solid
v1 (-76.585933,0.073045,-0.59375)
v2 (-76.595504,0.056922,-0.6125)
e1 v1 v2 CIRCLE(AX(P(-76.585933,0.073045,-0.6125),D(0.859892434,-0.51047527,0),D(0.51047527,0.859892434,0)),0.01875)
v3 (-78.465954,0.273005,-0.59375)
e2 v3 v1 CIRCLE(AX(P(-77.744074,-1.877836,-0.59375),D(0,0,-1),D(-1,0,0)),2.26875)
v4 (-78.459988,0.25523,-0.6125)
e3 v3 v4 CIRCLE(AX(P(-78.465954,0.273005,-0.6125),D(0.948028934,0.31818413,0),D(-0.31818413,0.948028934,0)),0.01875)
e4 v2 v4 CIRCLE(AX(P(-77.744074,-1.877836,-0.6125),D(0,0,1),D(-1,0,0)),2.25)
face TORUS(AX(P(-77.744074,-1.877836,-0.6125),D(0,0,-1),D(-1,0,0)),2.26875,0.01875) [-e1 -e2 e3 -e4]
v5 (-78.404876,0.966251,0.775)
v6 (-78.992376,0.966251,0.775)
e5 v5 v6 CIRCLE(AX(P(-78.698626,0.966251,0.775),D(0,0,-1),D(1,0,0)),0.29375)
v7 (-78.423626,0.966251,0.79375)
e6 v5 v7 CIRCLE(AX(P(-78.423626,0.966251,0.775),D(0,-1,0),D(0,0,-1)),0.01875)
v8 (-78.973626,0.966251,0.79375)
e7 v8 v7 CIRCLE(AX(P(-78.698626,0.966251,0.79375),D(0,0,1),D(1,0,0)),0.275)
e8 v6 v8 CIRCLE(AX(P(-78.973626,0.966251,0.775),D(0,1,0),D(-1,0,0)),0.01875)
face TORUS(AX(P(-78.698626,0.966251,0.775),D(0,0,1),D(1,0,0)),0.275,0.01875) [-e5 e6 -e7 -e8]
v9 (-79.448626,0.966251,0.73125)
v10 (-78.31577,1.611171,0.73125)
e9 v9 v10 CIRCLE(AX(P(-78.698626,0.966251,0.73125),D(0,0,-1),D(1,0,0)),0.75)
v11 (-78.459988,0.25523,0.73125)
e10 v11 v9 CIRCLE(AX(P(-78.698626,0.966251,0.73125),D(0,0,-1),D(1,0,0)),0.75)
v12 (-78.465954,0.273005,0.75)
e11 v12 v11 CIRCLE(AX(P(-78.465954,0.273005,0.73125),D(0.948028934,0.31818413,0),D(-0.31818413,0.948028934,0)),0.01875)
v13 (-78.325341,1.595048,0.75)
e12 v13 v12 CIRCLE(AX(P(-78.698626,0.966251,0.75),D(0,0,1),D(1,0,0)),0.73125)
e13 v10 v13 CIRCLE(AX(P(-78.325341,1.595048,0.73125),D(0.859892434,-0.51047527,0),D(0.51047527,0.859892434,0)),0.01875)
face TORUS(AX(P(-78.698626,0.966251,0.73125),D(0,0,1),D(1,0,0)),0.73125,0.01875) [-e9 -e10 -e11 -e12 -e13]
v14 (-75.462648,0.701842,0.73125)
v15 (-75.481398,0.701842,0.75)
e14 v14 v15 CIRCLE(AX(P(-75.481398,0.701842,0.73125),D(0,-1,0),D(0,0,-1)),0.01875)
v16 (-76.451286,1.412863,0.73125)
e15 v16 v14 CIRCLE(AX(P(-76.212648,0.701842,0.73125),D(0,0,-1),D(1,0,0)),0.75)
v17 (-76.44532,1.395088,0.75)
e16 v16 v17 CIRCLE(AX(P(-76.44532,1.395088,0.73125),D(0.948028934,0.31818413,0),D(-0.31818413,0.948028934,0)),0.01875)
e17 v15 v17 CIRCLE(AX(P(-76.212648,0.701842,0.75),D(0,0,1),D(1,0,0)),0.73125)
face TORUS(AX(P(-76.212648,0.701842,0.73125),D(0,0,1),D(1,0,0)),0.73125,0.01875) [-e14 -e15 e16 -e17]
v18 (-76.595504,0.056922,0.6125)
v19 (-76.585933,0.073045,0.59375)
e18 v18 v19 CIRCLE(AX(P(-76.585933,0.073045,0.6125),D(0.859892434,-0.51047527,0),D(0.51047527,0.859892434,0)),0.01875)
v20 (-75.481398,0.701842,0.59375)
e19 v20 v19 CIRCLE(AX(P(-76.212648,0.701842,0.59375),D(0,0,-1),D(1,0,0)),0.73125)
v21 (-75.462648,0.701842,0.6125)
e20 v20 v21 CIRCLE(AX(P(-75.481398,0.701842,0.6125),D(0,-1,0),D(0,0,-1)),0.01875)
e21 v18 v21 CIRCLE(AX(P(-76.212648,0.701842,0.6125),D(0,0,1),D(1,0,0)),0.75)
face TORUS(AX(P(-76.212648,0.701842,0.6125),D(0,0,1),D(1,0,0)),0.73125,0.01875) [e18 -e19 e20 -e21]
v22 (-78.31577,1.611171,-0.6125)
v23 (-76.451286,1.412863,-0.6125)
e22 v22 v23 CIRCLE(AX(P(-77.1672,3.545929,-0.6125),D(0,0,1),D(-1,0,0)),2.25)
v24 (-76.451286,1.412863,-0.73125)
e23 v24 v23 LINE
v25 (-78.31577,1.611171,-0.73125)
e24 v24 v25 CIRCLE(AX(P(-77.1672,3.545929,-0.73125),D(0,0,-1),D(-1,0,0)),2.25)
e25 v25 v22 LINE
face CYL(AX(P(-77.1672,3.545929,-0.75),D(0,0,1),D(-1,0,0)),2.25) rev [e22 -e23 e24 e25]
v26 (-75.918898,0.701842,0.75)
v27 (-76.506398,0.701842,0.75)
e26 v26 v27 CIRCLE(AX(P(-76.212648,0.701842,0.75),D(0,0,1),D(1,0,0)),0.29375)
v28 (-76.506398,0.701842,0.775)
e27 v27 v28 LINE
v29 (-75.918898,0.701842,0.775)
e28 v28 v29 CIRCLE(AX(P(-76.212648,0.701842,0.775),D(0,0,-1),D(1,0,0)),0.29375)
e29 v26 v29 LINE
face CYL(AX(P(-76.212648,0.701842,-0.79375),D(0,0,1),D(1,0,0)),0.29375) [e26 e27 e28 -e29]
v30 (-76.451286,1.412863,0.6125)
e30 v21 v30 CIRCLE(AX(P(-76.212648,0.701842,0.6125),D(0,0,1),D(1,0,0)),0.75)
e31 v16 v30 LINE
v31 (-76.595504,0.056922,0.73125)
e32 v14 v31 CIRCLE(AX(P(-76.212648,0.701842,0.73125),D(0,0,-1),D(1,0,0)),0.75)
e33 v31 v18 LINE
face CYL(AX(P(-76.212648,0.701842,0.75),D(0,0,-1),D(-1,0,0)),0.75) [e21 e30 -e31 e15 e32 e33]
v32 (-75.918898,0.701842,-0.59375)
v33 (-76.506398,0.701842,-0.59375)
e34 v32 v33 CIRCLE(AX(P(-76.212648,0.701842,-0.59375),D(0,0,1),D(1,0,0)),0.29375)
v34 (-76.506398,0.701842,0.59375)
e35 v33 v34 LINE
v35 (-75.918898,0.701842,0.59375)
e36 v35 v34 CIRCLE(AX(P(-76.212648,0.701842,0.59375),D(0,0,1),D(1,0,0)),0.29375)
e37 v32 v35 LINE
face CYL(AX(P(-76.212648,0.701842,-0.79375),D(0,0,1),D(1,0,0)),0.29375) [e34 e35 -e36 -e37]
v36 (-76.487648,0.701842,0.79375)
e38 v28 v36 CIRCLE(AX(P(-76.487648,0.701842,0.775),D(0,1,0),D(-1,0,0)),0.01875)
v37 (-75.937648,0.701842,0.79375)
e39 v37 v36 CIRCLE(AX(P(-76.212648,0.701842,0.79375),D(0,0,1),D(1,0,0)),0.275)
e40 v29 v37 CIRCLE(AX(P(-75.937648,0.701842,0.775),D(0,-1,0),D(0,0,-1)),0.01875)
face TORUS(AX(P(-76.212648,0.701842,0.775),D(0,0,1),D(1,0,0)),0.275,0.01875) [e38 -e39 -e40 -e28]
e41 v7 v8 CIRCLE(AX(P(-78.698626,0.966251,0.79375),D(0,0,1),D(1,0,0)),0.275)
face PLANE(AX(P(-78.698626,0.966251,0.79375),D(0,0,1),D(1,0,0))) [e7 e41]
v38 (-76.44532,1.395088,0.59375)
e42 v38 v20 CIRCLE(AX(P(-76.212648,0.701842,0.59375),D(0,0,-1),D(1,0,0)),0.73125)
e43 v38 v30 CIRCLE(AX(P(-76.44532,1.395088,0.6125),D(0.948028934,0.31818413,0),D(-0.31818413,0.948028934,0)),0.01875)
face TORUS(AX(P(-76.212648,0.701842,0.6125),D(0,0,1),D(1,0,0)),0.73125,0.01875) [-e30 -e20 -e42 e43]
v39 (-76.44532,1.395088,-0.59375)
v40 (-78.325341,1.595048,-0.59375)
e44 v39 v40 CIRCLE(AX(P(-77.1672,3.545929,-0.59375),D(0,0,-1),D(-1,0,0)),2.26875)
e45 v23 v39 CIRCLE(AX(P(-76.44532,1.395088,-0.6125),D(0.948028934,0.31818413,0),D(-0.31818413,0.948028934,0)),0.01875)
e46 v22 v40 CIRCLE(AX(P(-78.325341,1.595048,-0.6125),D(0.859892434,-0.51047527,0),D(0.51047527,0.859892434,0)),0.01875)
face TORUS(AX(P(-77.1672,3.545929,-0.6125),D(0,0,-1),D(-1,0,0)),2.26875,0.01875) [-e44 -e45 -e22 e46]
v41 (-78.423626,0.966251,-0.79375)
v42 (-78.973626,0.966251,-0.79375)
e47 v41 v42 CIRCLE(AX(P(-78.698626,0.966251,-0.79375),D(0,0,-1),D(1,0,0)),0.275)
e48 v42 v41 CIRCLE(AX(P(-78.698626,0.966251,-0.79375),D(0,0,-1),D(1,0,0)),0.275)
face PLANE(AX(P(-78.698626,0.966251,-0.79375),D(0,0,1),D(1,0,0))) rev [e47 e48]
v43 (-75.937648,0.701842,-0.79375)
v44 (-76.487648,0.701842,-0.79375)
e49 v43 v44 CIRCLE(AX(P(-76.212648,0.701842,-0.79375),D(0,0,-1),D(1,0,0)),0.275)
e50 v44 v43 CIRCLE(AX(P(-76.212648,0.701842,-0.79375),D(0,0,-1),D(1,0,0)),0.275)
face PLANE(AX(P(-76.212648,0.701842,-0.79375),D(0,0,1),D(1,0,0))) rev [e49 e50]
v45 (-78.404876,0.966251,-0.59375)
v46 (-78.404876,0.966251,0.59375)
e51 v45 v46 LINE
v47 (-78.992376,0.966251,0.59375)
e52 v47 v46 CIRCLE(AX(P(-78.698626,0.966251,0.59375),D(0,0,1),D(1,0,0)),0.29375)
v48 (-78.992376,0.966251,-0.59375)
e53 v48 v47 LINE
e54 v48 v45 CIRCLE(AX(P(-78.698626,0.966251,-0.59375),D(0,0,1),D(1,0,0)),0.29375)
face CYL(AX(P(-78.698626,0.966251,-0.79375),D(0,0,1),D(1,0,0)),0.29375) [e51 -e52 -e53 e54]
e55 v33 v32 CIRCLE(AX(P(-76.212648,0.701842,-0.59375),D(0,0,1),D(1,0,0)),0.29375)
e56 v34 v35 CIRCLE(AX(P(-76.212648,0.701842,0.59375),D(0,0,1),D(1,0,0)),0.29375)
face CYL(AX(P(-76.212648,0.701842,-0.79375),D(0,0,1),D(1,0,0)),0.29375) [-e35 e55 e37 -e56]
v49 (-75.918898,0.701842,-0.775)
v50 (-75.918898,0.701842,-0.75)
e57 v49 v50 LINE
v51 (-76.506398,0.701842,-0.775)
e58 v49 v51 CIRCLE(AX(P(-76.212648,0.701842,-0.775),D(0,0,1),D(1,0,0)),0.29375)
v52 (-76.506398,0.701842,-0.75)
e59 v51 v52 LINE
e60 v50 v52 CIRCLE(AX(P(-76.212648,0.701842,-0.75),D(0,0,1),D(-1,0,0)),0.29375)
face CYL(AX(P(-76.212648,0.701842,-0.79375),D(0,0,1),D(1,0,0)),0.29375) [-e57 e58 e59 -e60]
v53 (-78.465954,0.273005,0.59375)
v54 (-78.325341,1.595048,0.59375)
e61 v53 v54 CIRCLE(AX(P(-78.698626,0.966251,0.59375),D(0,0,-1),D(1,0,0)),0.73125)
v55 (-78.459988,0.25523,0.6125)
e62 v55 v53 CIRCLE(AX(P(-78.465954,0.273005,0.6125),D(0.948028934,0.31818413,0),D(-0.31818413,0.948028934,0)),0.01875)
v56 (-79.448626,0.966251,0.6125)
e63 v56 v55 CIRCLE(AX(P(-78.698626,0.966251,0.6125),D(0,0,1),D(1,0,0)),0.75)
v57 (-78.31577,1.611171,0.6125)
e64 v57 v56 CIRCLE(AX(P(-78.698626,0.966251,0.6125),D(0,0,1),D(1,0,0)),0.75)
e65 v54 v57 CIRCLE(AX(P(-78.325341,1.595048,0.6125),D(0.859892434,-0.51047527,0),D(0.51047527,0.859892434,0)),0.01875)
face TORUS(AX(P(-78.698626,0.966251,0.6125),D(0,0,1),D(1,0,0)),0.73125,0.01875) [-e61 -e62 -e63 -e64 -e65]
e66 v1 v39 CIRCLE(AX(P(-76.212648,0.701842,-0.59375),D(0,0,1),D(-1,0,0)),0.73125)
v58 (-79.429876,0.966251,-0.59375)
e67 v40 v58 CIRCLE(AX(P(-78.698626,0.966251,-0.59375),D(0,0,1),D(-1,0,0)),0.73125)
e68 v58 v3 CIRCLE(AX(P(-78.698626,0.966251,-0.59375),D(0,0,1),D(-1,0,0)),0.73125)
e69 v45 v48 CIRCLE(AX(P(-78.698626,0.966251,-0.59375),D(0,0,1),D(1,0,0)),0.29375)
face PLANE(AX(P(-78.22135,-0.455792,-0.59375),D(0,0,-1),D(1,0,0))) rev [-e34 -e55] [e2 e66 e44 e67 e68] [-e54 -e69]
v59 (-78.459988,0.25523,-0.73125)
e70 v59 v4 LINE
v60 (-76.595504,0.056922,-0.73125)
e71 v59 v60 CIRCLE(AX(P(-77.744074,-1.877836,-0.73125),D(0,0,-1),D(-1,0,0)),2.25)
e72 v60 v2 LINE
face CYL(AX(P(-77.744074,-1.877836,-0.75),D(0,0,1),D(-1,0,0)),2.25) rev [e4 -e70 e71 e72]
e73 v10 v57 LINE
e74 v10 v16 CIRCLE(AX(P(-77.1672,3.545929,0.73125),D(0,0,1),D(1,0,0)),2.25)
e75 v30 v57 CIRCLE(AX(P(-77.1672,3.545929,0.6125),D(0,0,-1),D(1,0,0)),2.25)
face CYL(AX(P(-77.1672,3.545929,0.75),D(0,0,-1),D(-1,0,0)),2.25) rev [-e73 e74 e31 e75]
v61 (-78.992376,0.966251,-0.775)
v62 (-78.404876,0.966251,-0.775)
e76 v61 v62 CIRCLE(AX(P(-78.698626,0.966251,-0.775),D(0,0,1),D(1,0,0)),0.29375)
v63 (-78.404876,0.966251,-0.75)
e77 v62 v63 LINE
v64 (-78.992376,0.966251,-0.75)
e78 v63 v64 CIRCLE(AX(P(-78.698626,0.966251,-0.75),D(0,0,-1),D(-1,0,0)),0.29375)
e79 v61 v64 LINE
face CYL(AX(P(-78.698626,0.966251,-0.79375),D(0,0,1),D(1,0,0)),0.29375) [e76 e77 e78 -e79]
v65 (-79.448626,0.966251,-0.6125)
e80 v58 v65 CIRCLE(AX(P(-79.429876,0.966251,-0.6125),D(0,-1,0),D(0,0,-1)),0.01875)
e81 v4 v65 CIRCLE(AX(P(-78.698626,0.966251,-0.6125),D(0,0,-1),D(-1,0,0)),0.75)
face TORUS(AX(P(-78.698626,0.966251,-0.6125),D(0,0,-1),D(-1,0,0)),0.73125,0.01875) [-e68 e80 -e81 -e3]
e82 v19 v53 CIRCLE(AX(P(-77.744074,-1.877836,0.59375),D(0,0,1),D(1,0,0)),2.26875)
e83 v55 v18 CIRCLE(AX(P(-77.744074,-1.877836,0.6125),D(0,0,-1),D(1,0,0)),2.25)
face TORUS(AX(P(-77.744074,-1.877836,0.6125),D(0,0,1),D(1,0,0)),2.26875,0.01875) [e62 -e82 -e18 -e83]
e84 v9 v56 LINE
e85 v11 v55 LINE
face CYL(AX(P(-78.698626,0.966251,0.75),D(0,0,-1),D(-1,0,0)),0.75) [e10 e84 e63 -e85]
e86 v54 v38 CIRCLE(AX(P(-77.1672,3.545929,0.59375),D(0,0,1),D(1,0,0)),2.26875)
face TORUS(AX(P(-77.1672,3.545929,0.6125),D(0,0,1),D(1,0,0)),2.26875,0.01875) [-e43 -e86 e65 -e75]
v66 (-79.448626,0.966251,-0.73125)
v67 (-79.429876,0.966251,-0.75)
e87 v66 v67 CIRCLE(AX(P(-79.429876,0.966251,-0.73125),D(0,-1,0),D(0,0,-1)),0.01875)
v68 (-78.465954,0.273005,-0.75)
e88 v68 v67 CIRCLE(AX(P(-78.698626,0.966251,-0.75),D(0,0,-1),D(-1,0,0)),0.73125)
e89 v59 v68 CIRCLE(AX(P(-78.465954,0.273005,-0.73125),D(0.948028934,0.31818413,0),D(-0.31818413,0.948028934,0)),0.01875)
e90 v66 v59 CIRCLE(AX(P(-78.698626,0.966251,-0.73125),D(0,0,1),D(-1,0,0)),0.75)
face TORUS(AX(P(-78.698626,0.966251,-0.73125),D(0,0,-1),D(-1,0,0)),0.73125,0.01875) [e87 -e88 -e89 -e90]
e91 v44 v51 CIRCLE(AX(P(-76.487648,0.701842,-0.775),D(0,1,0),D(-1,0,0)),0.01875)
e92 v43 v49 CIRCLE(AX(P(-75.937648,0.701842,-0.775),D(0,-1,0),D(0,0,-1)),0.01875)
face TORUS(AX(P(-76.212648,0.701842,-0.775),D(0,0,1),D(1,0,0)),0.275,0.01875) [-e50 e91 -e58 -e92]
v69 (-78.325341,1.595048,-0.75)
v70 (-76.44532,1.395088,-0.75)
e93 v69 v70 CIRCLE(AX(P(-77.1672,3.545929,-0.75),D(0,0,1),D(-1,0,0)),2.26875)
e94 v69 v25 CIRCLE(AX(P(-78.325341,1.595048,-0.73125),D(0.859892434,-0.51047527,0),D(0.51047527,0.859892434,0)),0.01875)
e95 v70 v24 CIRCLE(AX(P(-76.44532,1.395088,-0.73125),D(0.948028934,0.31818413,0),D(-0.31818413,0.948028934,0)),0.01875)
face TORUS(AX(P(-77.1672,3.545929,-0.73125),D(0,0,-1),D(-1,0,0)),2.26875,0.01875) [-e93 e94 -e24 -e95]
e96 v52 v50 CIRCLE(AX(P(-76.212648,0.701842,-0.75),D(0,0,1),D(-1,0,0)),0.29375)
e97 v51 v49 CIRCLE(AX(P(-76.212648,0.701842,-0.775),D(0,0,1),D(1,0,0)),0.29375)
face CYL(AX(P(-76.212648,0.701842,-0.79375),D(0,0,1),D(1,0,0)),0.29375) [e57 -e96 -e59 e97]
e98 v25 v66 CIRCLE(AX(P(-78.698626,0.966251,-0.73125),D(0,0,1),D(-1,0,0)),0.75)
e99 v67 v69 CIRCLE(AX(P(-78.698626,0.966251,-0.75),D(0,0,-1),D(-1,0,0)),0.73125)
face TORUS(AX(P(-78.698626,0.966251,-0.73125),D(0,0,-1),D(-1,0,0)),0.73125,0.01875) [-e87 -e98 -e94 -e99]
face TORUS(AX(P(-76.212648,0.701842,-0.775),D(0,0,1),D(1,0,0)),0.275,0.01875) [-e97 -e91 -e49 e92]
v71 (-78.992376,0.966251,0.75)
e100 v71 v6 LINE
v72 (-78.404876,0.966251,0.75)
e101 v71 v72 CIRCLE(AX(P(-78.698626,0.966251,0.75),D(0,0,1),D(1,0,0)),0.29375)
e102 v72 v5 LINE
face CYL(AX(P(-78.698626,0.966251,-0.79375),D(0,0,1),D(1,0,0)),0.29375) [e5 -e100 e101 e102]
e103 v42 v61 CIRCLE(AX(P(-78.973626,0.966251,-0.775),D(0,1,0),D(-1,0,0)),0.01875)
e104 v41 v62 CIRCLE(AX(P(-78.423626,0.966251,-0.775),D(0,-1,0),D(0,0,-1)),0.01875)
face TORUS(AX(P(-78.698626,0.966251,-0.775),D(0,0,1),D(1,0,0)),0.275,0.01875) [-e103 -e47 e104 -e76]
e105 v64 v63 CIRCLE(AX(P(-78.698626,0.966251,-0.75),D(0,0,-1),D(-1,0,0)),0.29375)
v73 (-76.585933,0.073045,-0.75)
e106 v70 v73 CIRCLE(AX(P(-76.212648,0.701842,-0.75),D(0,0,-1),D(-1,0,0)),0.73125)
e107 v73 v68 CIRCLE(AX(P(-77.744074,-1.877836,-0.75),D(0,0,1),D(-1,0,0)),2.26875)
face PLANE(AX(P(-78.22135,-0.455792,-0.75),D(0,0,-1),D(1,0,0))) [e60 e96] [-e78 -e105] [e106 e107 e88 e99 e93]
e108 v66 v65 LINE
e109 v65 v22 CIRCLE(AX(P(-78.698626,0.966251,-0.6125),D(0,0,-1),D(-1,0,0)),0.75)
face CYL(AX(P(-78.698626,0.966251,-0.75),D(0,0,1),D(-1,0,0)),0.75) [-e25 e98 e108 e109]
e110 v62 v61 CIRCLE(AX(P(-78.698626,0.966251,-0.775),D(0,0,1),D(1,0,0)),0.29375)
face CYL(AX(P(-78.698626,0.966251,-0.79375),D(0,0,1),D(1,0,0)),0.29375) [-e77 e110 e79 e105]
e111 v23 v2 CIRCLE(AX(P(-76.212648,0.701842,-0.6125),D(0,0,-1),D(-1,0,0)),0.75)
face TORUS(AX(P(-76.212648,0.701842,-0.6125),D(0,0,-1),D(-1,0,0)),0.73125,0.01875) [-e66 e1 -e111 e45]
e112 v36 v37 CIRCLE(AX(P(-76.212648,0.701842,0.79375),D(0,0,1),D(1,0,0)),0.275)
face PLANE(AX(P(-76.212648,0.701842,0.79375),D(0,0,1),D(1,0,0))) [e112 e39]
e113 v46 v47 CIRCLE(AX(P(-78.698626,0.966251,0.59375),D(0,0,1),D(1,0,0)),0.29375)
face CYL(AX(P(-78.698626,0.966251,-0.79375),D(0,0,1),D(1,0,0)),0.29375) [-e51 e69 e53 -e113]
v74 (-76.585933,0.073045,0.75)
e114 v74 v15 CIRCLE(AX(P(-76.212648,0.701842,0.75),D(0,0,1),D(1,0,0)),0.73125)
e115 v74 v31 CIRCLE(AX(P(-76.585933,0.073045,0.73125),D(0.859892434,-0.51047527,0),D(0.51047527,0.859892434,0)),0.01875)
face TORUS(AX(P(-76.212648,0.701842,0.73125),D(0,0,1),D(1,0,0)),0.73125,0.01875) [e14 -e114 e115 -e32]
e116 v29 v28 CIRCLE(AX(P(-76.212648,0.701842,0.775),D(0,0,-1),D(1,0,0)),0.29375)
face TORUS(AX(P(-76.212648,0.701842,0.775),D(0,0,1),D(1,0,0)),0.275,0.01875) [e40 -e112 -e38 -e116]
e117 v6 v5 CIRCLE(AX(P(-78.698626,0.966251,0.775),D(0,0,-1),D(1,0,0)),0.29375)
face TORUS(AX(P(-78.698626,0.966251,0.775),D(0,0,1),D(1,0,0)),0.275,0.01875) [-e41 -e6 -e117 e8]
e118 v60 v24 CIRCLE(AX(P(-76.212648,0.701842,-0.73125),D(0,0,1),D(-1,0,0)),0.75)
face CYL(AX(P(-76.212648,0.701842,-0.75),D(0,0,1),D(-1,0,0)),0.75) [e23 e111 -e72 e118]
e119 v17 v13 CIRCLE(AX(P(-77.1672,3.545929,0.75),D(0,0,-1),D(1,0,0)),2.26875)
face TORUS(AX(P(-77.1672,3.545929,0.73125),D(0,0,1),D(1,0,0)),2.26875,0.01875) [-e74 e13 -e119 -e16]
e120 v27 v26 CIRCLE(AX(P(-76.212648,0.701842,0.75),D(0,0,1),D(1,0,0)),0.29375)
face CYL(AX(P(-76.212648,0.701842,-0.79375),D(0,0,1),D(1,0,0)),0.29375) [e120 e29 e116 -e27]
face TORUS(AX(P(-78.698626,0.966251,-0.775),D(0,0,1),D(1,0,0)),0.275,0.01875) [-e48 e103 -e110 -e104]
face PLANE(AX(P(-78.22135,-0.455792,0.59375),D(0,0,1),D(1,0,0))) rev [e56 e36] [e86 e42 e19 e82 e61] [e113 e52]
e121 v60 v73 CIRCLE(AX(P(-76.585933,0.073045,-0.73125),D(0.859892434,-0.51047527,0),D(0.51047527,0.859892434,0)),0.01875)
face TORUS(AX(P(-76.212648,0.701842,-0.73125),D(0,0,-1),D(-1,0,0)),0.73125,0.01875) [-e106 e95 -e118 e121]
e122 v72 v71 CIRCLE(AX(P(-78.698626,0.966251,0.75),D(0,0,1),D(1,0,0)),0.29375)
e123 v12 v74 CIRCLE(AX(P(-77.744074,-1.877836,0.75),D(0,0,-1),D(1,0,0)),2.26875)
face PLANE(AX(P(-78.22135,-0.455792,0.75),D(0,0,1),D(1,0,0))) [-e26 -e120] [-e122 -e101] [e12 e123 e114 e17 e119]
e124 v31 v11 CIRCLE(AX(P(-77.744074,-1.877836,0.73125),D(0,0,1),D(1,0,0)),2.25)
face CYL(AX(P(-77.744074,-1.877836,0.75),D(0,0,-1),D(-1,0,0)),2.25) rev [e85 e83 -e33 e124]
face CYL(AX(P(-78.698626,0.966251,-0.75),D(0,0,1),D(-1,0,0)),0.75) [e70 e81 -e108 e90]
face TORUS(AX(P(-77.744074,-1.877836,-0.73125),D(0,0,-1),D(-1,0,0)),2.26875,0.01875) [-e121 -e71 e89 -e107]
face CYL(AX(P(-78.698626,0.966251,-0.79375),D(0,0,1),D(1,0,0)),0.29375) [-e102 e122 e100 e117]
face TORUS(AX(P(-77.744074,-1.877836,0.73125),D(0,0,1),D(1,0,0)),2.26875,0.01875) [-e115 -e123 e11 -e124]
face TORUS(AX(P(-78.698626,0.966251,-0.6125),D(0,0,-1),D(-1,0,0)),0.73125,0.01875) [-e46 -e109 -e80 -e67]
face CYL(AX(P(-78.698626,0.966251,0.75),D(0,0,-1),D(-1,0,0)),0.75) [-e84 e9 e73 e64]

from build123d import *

# Parameters (mm, degrees)
BOSS_EXTRUDE1_START      = 4.75
SKETCH3_R                = 2.35
BOSS_EXTRUDE1_DEPTH      = 1.25
BOSS_EXTRUDE2_DEPTH      = 6.35
BOSS_EXTRUDE2_DEPTH_BACK = 6.35
SKETCH4_R                = 2.35
FILLET1_R                = 0.15
SCALE1_SCALE             = 0.5
SCALE2_SCALE             = 0.5
SCALE3_SCALE             = 0.5


with BuildPart() as part:
    # Sketch3 → Boss-Extrude1 (new body)
    with BuildSketch(Plane.XY.offset(BOSS_EXTRUDE1_START)):
        with BuildLine():
            ThreePointArc((-70.574575747, -5.382946104), (-61.545376441, -0.858174297), (-69.420828904, 5.464582104))
            ThreePointArc((-69.420828904, 5.464582104), (-77.051891637, 4.630059865), (-84.336698111, 7.0510391))
            ThreePointArc((-84.336698111, 7.0510391), (-93.365897416, 2.526267293), (-85.490444954, -3.796489108))
            ThreePointArc((-85.490444954, -3.796489108), (-77.85938222, -2.961966869), (-70.574575747, -5.382946104))
        make_face()
        with Locations((-87.399549733, 1.891684495)):
            Circle(SKETCH3_R, mode=Mode.SUBTRACT)
        with Locations((-67.511724124, -0.223591499)):
            Circle(SKETCH3_R, mode=Mode.SUBTRACT)
    extrude(amount=BOSS_EXTRUDE1_DEPTH)


with BuildPart() as body_2:
    # Mirror1: mirrored copy
    add(part.part.mirror(Plane.XY))


with BuildPart() as part_1:
    add(part.part)

    add(body_2.part)  # Boss-Extrude2 merges body 2
    # Sketch4 → Boss-Extrude2 (add, two sides: drawn at the far end of the back side and taken through both)
    with BuildSketch(Plane.XY.offset(-BOSS_EXTRUDE2_DEPTH_BACK)):
        with Locations((-67.511724124, -0.223591499)):
            Circle(SKETCH4_R)
        with Locations((-87.399549733, 1.891684495)):
            Circle(SKETCH4_R)
    extrude(amount=BOSS_EXTRUDE2_DEPTH + BOSS_EXTRUDE2_DEPTH_BACK)

    # Fillet1
    fillet1_edges = [part_1.edges().sort_by_distance(p)[0] for p in [
        (-77.051891637, 4.630059865, 6),
        (-93.365897416, 2.526267293, 6),
        (-69.861724124, -0.223591499, -6.35),
        (-69.861724124, -0.223591499, 6.35),
        (-77.85938222, -2.961966869, -4.75),
        (-61.545376441, -0.858174297, -4.75),
        (-77.051891637, 4.630059865, -4.75),
        (-93.365897416, 2.526267293, -4.75),
        (-77.85938222, -2.961966869, -6),
        (-61.545376441, -0.858174297, -6),
        (-77.051891637, 4.630059865, -6),
        (-93.365897416, 2.526267293, -6),
        (-89.749549733, 1.891684495, -6.35),
        (-89.749549733, 1.891684495, 6.35),
        (-77.85938222, -2.961966869, 6),
        (-93.365897416, 2.526267293, 4.75),
        (-77.051891637, 4.630059865, 4.75),
        (-61.545376441, -0.858174297, 4.75),
        (-77.85938222, -2.961966869, 4.75),
        (-61.545376441, -0.858174297, 6),
    ]]
    fillet(fillet1_edges, radius=FILLET1_R)


with BuildPart() as part_2:
    # Scale1: scaled about (-77.455636929, 0.834046498, 0)
    add(part_1.part.scale(SCALE1_SCALE).moved(Location((-38.727818464, 0.417023249, 0))))


with BuildPart() as part_3:
    # Scale2: scaled about (-77.455636929, 0.834046498, 0)
    add(part_2.part.scale(SCALE2_SCALE).moved(Location((-38.727818464, 0.417023249, 0))))


with BuildPart() as part_4:
    # Scale3: scaled about (-77.455636929, 0.834046498, 0)
    add(part_3.part.scale(SCALE3_SCALE).moved(Location((-38.727818464, 0.417023249, 0))))


solid = part_4.part
